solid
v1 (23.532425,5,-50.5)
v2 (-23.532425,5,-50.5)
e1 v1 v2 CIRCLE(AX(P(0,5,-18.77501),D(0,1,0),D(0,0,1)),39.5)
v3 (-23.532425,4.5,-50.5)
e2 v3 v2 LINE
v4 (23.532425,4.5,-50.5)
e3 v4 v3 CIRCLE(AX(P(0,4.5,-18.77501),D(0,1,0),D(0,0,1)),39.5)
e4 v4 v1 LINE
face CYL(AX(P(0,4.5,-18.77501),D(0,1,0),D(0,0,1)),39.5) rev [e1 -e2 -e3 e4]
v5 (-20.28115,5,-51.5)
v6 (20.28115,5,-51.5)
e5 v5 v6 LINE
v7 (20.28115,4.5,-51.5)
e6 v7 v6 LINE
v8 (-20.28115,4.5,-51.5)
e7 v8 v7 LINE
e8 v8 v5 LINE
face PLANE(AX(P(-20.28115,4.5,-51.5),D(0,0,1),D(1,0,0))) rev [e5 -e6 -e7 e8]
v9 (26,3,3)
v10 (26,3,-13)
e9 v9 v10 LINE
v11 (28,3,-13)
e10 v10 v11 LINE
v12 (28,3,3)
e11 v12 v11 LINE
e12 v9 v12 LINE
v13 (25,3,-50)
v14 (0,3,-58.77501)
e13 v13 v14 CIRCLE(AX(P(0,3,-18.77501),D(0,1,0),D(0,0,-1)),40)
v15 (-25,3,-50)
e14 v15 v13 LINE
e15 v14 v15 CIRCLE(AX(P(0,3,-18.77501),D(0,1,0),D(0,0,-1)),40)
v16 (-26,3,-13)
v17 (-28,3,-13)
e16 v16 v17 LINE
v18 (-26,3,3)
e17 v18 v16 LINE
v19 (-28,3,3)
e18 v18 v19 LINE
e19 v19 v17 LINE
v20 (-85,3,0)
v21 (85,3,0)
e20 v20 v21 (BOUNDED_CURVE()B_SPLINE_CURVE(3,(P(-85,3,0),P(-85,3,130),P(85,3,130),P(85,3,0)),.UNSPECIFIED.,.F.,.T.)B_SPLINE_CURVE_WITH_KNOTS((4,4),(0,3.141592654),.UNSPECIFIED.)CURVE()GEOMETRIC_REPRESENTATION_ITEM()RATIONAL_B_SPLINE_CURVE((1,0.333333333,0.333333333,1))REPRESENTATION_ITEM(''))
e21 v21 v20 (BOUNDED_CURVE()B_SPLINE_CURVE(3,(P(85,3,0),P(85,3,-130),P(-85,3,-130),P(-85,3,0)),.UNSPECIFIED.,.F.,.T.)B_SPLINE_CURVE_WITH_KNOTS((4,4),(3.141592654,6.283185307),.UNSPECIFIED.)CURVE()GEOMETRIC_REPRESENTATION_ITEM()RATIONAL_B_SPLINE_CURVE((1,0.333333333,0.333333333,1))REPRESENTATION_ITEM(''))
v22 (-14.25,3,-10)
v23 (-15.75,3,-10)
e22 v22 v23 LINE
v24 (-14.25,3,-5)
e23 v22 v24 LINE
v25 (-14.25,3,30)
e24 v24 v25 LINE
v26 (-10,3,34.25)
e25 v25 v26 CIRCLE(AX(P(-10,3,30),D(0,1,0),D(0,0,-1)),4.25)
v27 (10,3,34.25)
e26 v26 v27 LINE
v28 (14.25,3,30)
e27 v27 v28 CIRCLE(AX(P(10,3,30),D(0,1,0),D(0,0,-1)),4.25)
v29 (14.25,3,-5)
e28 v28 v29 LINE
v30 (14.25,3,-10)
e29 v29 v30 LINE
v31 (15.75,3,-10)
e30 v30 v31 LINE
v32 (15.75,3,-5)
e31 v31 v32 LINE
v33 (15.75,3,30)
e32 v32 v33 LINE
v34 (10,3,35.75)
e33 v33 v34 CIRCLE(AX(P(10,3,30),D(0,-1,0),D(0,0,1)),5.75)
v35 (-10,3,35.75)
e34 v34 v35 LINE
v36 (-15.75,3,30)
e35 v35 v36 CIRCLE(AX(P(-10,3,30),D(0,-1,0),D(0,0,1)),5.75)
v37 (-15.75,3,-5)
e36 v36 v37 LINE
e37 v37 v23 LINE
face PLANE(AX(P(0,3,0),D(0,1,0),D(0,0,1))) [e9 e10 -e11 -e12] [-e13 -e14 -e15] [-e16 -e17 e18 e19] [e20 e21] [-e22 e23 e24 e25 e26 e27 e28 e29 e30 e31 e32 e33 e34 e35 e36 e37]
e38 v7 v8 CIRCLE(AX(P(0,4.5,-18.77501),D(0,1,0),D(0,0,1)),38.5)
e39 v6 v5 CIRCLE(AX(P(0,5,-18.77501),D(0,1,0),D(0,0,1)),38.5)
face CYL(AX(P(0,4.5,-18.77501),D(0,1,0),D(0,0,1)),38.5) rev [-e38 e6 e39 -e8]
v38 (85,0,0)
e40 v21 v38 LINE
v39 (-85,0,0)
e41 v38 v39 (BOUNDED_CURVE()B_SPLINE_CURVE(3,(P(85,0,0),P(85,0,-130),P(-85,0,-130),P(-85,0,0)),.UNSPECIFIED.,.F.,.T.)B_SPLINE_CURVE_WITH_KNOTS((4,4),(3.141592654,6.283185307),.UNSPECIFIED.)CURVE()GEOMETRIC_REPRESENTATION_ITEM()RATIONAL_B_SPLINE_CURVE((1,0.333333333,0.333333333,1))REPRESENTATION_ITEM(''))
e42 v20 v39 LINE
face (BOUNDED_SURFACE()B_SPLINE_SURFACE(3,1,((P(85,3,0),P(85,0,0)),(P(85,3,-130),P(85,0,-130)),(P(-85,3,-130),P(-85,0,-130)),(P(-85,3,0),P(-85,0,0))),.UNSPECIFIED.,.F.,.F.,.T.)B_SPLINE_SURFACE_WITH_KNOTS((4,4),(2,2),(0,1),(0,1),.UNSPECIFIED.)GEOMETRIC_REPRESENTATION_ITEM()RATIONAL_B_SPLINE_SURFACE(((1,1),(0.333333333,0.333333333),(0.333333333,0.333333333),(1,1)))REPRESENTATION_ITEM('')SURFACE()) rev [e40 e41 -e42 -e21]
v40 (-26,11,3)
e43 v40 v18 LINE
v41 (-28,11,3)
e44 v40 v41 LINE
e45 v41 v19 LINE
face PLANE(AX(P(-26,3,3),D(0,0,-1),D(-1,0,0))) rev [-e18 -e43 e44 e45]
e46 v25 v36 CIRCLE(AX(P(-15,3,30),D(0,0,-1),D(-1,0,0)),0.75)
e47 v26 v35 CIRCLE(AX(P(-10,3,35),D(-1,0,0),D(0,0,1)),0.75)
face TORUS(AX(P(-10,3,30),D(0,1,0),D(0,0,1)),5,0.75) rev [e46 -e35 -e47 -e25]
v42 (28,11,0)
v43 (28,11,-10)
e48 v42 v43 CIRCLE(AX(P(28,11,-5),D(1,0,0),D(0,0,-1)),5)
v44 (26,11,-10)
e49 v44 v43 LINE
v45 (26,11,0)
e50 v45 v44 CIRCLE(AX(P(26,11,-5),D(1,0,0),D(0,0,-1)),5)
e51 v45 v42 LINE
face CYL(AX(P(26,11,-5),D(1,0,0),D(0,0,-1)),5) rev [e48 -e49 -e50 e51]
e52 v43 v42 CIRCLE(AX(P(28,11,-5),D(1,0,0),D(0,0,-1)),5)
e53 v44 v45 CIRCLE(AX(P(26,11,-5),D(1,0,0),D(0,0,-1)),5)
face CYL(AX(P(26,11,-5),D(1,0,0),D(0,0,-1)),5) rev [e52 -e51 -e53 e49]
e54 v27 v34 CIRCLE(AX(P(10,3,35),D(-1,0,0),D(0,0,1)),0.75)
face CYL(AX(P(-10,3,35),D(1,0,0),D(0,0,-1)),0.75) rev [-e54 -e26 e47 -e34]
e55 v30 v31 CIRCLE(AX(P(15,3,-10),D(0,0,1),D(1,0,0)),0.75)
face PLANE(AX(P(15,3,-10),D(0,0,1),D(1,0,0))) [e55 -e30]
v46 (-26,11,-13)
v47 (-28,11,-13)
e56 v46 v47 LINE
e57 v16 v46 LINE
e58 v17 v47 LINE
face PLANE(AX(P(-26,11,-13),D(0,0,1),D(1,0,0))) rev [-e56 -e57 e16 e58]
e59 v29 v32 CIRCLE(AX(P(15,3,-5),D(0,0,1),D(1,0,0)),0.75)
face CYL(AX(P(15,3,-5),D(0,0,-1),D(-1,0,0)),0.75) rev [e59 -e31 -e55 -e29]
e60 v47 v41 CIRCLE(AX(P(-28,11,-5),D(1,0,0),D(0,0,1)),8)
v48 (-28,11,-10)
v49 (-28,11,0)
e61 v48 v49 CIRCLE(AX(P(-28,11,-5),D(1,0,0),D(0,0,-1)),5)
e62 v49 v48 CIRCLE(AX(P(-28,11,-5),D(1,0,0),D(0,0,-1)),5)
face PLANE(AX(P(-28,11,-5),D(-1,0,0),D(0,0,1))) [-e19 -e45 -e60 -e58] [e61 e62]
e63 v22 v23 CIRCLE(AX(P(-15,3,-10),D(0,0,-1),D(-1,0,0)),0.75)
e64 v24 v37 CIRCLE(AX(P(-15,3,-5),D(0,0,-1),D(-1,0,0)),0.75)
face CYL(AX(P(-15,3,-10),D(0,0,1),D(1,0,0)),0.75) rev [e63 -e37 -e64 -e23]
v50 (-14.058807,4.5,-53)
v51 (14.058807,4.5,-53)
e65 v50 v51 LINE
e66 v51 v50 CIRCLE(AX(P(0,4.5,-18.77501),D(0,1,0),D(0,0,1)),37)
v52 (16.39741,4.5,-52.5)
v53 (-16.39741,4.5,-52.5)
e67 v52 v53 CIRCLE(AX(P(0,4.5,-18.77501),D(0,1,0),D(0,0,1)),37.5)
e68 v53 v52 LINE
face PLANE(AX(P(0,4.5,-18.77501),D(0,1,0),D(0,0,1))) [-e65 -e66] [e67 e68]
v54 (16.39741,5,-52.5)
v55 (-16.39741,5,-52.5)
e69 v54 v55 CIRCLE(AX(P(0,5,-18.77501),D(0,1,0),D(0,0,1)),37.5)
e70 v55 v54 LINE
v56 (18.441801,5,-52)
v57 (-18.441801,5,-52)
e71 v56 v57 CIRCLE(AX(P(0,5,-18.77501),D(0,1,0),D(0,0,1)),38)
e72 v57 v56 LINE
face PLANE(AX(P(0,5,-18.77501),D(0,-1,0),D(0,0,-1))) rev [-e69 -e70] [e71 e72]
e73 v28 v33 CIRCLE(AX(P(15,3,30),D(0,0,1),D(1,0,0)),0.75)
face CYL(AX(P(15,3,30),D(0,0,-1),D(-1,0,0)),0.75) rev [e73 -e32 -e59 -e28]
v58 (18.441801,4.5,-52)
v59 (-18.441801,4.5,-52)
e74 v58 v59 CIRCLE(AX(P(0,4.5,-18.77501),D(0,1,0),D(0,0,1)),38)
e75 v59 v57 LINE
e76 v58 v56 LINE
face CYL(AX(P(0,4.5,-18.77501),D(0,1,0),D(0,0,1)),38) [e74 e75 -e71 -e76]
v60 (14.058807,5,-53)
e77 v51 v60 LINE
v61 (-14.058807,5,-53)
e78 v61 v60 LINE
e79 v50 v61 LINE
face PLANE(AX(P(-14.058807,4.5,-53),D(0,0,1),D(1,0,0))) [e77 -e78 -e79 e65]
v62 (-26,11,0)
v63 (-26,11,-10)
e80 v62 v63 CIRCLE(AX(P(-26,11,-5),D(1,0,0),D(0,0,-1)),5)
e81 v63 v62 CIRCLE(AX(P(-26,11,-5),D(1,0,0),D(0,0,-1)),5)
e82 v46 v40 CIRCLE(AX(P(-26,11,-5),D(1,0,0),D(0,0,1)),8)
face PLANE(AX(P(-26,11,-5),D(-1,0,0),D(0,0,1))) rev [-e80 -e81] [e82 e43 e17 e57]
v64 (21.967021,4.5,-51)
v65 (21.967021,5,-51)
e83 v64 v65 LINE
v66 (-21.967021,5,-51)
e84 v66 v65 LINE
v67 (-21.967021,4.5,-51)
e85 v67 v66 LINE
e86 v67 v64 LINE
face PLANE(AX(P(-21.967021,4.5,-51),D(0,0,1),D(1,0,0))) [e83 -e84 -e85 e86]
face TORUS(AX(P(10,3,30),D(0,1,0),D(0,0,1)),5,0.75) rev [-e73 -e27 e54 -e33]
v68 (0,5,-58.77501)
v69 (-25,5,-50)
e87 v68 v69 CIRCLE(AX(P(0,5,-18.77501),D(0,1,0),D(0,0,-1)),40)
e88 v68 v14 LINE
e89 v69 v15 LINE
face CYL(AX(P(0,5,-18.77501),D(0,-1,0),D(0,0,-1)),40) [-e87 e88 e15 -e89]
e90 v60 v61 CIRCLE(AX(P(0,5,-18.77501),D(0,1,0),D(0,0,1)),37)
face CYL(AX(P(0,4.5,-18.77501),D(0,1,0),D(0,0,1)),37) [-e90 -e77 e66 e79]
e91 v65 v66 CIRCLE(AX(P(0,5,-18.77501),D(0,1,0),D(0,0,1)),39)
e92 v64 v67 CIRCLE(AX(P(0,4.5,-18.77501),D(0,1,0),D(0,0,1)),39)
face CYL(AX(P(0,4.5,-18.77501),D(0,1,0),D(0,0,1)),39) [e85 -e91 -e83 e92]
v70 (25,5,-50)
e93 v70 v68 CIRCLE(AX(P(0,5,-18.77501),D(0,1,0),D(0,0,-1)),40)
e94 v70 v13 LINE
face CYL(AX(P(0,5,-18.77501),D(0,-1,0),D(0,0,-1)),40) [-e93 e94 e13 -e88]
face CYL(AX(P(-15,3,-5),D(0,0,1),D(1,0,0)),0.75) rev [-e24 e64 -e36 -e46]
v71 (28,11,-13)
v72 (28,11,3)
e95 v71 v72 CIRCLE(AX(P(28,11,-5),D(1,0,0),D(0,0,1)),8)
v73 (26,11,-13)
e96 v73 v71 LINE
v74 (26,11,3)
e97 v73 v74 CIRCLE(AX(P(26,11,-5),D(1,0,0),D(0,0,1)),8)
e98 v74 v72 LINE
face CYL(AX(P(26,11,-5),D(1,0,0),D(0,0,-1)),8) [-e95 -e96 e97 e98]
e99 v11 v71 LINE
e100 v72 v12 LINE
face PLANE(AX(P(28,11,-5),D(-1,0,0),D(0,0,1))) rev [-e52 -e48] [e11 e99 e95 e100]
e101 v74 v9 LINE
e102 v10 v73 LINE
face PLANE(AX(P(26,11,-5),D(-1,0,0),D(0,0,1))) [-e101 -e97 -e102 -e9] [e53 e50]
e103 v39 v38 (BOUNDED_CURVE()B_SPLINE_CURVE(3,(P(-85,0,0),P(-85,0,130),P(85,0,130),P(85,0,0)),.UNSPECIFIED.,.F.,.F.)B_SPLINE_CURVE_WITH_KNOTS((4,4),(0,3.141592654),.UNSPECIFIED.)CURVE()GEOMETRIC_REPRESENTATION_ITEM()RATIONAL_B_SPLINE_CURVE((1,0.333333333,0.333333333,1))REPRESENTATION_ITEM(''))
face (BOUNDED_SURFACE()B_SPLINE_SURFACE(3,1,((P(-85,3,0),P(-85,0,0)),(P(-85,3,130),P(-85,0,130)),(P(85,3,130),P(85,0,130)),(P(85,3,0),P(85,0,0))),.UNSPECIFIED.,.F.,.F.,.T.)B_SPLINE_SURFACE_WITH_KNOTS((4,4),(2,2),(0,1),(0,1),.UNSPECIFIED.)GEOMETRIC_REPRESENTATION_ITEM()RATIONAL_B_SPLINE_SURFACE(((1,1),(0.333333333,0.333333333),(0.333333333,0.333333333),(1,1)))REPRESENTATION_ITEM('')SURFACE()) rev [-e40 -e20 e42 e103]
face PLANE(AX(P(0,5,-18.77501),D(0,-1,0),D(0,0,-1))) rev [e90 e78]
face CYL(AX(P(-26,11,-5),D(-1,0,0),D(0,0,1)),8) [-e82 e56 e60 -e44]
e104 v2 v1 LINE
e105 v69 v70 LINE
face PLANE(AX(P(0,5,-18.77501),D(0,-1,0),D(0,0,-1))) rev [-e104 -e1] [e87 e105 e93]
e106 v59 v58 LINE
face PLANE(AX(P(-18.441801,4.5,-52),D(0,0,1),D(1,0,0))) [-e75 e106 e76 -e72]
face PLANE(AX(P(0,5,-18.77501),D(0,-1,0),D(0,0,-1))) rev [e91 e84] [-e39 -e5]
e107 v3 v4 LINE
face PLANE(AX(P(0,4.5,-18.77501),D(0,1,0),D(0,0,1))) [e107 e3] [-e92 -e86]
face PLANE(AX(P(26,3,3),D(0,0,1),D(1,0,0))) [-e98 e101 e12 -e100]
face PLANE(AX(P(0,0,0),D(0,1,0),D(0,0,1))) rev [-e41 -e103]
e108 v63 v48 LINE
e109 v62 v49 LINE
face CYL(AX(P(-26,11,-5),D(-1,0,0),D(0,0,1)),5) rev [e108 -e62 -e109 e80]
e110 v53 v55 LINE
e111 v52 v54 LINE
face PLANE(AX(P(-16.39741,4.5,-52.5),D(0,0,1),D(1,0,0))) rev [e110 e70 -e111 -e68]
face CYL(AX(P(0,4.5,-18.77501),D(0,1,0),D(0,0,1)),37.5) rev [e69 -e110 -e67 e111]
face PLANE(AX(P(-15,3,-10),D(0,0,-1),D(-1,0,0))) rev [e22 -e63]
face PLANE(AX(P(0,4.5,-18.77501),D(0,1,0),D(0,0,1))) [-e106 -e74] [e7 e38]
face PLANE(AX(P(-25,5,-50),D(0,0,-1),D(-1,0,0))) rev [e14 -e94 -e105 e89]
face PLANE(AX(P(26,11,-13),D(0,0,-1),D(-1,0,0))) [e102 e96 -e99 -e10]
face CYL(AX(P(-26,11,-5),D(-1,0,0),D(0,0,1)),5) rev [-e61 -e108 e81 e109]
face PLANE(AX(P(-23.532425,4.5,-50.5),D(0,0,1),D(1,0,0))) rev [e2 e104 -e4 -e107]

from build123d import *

# Parameters (mm, degrees)
SKETCH1_RX           = 85
SKETCH1_RY           = 65
BOSS_EXTRUDE1_DEPTH  = 3
BOSS_EXTRUDE2_START  = 28
SKETCH_2_2_R         = 5
BOSS_EXTRUDE2_DEPTH  = 2
BOSS_EXTRUDE3_START  = -26
SKETCH_2_2_2_R       = 5
BOSS_EXTRUDE3_DEPTH  = 2
CUT_SWEEP1_PROFILE_R = 0.75
BOSS_EXTRUDE4_DEPTH  = 2
CUT_EXTRUDE1_DEPTH   = 0.5
CUT_EXTRUDE2_DEPTH   = 0.5
CUT_EXTRUDE3_DEPTH   = 0.5


with BuildPart() as part:
    # Sketch1 → Boss-Extrude1 (new body)
    with BuildSketch(Plane(origin=(0, 0, 0), x_dir=(1, 0, 0), z_dir=(0, 1, 0))):
        with Locations(Location((0, 0), (0, 0, 180))):
            Ellipse(SKETCH1_RX, SKETCH1_RY)
    extrude(amount=BOSS_EXTRUDE1_DEPTH)

    # Sketch 2_2 → Boss-Extrude2 (add)
    with BuildSketch(Plane(origin=(0, 0, 0), x_dir=(0, 0, -1), z_dir=(1, 0, 0)).offset(BOSS_EXTRUDE2_START)):
        with BuildLine():
            Line((-3, 3), (-3, 11))
            ThreePointArc((-3, 11), (5, 19), (13, 11))
            Line((13, 11), (13, 3))
            Line((13, 3), (-3, 3))
        make_face()
        with Locations((5, 11)):
            Circle(SKETCH_2_2_R, mode=Mode.SUBTRACT)
    extrude(amount=-BOSS_EXTRUDE2_DEPTH)

    # Sketch 2_2 2 → Boss-Extrude3 (add)
    with BuildSketch(Plane(origin=(0, 0, 0), x_dir=(0, 0, -1), z_dir=(1, 0, 0)).offset(BOSS_EXTRUDE3_START)):
        with BuildLine():
            Line((-3, 3), (-3, 11))
            ThreePointArc((-3, 11), (5, 19), (13, 11))
            Line((13, 11), (13, 3))
            Line((13, 3), (-3, 3))
        make_face()
        with Locations((5, 11)):
            Circle(SKETCH_2_2_2_R, mode=Mode.SUBTRACT)
    extrude(amount=-BOSS_EXTRUDE3_DEPTH)

    # Cut-Sweep1: sweep along a path in Sketch3
    with BuildLine(Plane(origin=(0, 3, 0), x_dir=(1, 0, 0), z_dir=(0, 1, 0))) as cut_sweep1_path:
        Line((-15, 10), (-15, 5))
        Line((-15, 5), (-15, -30))
        ThreePointArc((-15, -30), (-13.535533906, -33.535533906), (-10, -35))
        Line((-10, -35), (10, -35))
        ThreePointArc((10, -35), (13.535533906, -33.535533906), (15, -30))
        Line((15, -30), (15, 5))
        Line((15, 5), (15, 10))
    # Cut-Sweep1 profile (on start of the path) → Cut-Sweep1 (sweep, cut)
    with BuildSketch(Plane(origin=(-15, 3, -10), x_dir=(1, 0, 0), z_dir=(0, 0, 1))):
        Circle(CUT_SWEEP1_PROFILE_R)
    sweep(path=cut_sweep1_path.line, mode=Mode.SUBTRACT)

    # Sketch23 → Boss-Extrude4 (add)
    with BuildSketch(Plane(origin=(0, 3, 0), x_dir=(1, 0, 0), z_dir=(0, 1, 0))):
        with BuildLine():
            Line((-25, 50), (25, 50))
            ThreePointArc((25, 50), (0, 58.775010008), (-25, 50))
        make_face()
    extrude(amount=BOSS_EXTRUDE4_DEPTH)

    # Sketch24 → Cut-Extrude1 (cut)
    with BuildSketch(Plane(origin=(0, 5, 0), x_dir=(1, 0, 0), z_dir=(0, 1, 0))):
        with BuildLine():
            Line((-23.532424652, 50.5), (23.532424652, 50.5))
            ThreePointArc((23.532424652, 50.5), (0, 58.275010008), (-23.532424652, 50.5))
        make_face()
        with BuildLine():
            Line((-21.967021191, 51), (21.967021191, 51))
            ThreePointArc((21.967021191, 51), (0, 57.775010008), (-21.967021191, 51))
        make_face(mode=Mode.SUBTRACT)
    extrude(amount=-CUT_EXTRUDE1_DEPTH, mode=Mode.SUBTRACT)

    # Sketch25 → Cut-Extrude2 (cut)
    with BuildSketch(Plane(origin=(0, 5, 0), x_dir=(1, 0, 0), z_dir=(0, 1, 0))):
        with BuildLine():
            Line((-20.281149623, 51.5), (20.281149623, 51.5))
            ThreePointArc((20.281149623, 51.5), (0, 57.275010008), (-20.281149623, 51.5))
        make_face()
        with BuildLine():
            Line((-18.441801431, 52), (18.441801431, 52))
            ThreePointArc((18.441801431, 52), (0, 56.775010008), (-18.441801431, 52))
        make_face(mode=Mode.SUBTRACT)
    extrude(amount=-CUT_EXTRUDE2_DEPTH, mode=Mode.SUBTRACT)

    # Sketch26 → Cut-Extrude3 (cut)
    with BuildSketch(Plane(origin=(0, 5, 0), x_dir=(1, 0, 0), z_dir=(0, 1, 0))):
        with BuildLine():
            Line((-16.397409858, 52.5), (16.397409858, 52.5))
            ThreePointArc((16.397409858, 52.5), (0, 56.275010008), (-16.397409858, 52.5))
        make_face()
        with BuildLine():
            Line((-14.058807206, 53), (14.058807206, 53))
            ThreePointArc((14.058807206, 53), (0, 55.775010008), (-14.058807206, 53))
        make_face(mode=Mode.SUBTRACT)
    extrude(amount=-CUT_EXTRUDE3_DEPTH, mode=Mode.SUBTRACT)


solid = part.part
